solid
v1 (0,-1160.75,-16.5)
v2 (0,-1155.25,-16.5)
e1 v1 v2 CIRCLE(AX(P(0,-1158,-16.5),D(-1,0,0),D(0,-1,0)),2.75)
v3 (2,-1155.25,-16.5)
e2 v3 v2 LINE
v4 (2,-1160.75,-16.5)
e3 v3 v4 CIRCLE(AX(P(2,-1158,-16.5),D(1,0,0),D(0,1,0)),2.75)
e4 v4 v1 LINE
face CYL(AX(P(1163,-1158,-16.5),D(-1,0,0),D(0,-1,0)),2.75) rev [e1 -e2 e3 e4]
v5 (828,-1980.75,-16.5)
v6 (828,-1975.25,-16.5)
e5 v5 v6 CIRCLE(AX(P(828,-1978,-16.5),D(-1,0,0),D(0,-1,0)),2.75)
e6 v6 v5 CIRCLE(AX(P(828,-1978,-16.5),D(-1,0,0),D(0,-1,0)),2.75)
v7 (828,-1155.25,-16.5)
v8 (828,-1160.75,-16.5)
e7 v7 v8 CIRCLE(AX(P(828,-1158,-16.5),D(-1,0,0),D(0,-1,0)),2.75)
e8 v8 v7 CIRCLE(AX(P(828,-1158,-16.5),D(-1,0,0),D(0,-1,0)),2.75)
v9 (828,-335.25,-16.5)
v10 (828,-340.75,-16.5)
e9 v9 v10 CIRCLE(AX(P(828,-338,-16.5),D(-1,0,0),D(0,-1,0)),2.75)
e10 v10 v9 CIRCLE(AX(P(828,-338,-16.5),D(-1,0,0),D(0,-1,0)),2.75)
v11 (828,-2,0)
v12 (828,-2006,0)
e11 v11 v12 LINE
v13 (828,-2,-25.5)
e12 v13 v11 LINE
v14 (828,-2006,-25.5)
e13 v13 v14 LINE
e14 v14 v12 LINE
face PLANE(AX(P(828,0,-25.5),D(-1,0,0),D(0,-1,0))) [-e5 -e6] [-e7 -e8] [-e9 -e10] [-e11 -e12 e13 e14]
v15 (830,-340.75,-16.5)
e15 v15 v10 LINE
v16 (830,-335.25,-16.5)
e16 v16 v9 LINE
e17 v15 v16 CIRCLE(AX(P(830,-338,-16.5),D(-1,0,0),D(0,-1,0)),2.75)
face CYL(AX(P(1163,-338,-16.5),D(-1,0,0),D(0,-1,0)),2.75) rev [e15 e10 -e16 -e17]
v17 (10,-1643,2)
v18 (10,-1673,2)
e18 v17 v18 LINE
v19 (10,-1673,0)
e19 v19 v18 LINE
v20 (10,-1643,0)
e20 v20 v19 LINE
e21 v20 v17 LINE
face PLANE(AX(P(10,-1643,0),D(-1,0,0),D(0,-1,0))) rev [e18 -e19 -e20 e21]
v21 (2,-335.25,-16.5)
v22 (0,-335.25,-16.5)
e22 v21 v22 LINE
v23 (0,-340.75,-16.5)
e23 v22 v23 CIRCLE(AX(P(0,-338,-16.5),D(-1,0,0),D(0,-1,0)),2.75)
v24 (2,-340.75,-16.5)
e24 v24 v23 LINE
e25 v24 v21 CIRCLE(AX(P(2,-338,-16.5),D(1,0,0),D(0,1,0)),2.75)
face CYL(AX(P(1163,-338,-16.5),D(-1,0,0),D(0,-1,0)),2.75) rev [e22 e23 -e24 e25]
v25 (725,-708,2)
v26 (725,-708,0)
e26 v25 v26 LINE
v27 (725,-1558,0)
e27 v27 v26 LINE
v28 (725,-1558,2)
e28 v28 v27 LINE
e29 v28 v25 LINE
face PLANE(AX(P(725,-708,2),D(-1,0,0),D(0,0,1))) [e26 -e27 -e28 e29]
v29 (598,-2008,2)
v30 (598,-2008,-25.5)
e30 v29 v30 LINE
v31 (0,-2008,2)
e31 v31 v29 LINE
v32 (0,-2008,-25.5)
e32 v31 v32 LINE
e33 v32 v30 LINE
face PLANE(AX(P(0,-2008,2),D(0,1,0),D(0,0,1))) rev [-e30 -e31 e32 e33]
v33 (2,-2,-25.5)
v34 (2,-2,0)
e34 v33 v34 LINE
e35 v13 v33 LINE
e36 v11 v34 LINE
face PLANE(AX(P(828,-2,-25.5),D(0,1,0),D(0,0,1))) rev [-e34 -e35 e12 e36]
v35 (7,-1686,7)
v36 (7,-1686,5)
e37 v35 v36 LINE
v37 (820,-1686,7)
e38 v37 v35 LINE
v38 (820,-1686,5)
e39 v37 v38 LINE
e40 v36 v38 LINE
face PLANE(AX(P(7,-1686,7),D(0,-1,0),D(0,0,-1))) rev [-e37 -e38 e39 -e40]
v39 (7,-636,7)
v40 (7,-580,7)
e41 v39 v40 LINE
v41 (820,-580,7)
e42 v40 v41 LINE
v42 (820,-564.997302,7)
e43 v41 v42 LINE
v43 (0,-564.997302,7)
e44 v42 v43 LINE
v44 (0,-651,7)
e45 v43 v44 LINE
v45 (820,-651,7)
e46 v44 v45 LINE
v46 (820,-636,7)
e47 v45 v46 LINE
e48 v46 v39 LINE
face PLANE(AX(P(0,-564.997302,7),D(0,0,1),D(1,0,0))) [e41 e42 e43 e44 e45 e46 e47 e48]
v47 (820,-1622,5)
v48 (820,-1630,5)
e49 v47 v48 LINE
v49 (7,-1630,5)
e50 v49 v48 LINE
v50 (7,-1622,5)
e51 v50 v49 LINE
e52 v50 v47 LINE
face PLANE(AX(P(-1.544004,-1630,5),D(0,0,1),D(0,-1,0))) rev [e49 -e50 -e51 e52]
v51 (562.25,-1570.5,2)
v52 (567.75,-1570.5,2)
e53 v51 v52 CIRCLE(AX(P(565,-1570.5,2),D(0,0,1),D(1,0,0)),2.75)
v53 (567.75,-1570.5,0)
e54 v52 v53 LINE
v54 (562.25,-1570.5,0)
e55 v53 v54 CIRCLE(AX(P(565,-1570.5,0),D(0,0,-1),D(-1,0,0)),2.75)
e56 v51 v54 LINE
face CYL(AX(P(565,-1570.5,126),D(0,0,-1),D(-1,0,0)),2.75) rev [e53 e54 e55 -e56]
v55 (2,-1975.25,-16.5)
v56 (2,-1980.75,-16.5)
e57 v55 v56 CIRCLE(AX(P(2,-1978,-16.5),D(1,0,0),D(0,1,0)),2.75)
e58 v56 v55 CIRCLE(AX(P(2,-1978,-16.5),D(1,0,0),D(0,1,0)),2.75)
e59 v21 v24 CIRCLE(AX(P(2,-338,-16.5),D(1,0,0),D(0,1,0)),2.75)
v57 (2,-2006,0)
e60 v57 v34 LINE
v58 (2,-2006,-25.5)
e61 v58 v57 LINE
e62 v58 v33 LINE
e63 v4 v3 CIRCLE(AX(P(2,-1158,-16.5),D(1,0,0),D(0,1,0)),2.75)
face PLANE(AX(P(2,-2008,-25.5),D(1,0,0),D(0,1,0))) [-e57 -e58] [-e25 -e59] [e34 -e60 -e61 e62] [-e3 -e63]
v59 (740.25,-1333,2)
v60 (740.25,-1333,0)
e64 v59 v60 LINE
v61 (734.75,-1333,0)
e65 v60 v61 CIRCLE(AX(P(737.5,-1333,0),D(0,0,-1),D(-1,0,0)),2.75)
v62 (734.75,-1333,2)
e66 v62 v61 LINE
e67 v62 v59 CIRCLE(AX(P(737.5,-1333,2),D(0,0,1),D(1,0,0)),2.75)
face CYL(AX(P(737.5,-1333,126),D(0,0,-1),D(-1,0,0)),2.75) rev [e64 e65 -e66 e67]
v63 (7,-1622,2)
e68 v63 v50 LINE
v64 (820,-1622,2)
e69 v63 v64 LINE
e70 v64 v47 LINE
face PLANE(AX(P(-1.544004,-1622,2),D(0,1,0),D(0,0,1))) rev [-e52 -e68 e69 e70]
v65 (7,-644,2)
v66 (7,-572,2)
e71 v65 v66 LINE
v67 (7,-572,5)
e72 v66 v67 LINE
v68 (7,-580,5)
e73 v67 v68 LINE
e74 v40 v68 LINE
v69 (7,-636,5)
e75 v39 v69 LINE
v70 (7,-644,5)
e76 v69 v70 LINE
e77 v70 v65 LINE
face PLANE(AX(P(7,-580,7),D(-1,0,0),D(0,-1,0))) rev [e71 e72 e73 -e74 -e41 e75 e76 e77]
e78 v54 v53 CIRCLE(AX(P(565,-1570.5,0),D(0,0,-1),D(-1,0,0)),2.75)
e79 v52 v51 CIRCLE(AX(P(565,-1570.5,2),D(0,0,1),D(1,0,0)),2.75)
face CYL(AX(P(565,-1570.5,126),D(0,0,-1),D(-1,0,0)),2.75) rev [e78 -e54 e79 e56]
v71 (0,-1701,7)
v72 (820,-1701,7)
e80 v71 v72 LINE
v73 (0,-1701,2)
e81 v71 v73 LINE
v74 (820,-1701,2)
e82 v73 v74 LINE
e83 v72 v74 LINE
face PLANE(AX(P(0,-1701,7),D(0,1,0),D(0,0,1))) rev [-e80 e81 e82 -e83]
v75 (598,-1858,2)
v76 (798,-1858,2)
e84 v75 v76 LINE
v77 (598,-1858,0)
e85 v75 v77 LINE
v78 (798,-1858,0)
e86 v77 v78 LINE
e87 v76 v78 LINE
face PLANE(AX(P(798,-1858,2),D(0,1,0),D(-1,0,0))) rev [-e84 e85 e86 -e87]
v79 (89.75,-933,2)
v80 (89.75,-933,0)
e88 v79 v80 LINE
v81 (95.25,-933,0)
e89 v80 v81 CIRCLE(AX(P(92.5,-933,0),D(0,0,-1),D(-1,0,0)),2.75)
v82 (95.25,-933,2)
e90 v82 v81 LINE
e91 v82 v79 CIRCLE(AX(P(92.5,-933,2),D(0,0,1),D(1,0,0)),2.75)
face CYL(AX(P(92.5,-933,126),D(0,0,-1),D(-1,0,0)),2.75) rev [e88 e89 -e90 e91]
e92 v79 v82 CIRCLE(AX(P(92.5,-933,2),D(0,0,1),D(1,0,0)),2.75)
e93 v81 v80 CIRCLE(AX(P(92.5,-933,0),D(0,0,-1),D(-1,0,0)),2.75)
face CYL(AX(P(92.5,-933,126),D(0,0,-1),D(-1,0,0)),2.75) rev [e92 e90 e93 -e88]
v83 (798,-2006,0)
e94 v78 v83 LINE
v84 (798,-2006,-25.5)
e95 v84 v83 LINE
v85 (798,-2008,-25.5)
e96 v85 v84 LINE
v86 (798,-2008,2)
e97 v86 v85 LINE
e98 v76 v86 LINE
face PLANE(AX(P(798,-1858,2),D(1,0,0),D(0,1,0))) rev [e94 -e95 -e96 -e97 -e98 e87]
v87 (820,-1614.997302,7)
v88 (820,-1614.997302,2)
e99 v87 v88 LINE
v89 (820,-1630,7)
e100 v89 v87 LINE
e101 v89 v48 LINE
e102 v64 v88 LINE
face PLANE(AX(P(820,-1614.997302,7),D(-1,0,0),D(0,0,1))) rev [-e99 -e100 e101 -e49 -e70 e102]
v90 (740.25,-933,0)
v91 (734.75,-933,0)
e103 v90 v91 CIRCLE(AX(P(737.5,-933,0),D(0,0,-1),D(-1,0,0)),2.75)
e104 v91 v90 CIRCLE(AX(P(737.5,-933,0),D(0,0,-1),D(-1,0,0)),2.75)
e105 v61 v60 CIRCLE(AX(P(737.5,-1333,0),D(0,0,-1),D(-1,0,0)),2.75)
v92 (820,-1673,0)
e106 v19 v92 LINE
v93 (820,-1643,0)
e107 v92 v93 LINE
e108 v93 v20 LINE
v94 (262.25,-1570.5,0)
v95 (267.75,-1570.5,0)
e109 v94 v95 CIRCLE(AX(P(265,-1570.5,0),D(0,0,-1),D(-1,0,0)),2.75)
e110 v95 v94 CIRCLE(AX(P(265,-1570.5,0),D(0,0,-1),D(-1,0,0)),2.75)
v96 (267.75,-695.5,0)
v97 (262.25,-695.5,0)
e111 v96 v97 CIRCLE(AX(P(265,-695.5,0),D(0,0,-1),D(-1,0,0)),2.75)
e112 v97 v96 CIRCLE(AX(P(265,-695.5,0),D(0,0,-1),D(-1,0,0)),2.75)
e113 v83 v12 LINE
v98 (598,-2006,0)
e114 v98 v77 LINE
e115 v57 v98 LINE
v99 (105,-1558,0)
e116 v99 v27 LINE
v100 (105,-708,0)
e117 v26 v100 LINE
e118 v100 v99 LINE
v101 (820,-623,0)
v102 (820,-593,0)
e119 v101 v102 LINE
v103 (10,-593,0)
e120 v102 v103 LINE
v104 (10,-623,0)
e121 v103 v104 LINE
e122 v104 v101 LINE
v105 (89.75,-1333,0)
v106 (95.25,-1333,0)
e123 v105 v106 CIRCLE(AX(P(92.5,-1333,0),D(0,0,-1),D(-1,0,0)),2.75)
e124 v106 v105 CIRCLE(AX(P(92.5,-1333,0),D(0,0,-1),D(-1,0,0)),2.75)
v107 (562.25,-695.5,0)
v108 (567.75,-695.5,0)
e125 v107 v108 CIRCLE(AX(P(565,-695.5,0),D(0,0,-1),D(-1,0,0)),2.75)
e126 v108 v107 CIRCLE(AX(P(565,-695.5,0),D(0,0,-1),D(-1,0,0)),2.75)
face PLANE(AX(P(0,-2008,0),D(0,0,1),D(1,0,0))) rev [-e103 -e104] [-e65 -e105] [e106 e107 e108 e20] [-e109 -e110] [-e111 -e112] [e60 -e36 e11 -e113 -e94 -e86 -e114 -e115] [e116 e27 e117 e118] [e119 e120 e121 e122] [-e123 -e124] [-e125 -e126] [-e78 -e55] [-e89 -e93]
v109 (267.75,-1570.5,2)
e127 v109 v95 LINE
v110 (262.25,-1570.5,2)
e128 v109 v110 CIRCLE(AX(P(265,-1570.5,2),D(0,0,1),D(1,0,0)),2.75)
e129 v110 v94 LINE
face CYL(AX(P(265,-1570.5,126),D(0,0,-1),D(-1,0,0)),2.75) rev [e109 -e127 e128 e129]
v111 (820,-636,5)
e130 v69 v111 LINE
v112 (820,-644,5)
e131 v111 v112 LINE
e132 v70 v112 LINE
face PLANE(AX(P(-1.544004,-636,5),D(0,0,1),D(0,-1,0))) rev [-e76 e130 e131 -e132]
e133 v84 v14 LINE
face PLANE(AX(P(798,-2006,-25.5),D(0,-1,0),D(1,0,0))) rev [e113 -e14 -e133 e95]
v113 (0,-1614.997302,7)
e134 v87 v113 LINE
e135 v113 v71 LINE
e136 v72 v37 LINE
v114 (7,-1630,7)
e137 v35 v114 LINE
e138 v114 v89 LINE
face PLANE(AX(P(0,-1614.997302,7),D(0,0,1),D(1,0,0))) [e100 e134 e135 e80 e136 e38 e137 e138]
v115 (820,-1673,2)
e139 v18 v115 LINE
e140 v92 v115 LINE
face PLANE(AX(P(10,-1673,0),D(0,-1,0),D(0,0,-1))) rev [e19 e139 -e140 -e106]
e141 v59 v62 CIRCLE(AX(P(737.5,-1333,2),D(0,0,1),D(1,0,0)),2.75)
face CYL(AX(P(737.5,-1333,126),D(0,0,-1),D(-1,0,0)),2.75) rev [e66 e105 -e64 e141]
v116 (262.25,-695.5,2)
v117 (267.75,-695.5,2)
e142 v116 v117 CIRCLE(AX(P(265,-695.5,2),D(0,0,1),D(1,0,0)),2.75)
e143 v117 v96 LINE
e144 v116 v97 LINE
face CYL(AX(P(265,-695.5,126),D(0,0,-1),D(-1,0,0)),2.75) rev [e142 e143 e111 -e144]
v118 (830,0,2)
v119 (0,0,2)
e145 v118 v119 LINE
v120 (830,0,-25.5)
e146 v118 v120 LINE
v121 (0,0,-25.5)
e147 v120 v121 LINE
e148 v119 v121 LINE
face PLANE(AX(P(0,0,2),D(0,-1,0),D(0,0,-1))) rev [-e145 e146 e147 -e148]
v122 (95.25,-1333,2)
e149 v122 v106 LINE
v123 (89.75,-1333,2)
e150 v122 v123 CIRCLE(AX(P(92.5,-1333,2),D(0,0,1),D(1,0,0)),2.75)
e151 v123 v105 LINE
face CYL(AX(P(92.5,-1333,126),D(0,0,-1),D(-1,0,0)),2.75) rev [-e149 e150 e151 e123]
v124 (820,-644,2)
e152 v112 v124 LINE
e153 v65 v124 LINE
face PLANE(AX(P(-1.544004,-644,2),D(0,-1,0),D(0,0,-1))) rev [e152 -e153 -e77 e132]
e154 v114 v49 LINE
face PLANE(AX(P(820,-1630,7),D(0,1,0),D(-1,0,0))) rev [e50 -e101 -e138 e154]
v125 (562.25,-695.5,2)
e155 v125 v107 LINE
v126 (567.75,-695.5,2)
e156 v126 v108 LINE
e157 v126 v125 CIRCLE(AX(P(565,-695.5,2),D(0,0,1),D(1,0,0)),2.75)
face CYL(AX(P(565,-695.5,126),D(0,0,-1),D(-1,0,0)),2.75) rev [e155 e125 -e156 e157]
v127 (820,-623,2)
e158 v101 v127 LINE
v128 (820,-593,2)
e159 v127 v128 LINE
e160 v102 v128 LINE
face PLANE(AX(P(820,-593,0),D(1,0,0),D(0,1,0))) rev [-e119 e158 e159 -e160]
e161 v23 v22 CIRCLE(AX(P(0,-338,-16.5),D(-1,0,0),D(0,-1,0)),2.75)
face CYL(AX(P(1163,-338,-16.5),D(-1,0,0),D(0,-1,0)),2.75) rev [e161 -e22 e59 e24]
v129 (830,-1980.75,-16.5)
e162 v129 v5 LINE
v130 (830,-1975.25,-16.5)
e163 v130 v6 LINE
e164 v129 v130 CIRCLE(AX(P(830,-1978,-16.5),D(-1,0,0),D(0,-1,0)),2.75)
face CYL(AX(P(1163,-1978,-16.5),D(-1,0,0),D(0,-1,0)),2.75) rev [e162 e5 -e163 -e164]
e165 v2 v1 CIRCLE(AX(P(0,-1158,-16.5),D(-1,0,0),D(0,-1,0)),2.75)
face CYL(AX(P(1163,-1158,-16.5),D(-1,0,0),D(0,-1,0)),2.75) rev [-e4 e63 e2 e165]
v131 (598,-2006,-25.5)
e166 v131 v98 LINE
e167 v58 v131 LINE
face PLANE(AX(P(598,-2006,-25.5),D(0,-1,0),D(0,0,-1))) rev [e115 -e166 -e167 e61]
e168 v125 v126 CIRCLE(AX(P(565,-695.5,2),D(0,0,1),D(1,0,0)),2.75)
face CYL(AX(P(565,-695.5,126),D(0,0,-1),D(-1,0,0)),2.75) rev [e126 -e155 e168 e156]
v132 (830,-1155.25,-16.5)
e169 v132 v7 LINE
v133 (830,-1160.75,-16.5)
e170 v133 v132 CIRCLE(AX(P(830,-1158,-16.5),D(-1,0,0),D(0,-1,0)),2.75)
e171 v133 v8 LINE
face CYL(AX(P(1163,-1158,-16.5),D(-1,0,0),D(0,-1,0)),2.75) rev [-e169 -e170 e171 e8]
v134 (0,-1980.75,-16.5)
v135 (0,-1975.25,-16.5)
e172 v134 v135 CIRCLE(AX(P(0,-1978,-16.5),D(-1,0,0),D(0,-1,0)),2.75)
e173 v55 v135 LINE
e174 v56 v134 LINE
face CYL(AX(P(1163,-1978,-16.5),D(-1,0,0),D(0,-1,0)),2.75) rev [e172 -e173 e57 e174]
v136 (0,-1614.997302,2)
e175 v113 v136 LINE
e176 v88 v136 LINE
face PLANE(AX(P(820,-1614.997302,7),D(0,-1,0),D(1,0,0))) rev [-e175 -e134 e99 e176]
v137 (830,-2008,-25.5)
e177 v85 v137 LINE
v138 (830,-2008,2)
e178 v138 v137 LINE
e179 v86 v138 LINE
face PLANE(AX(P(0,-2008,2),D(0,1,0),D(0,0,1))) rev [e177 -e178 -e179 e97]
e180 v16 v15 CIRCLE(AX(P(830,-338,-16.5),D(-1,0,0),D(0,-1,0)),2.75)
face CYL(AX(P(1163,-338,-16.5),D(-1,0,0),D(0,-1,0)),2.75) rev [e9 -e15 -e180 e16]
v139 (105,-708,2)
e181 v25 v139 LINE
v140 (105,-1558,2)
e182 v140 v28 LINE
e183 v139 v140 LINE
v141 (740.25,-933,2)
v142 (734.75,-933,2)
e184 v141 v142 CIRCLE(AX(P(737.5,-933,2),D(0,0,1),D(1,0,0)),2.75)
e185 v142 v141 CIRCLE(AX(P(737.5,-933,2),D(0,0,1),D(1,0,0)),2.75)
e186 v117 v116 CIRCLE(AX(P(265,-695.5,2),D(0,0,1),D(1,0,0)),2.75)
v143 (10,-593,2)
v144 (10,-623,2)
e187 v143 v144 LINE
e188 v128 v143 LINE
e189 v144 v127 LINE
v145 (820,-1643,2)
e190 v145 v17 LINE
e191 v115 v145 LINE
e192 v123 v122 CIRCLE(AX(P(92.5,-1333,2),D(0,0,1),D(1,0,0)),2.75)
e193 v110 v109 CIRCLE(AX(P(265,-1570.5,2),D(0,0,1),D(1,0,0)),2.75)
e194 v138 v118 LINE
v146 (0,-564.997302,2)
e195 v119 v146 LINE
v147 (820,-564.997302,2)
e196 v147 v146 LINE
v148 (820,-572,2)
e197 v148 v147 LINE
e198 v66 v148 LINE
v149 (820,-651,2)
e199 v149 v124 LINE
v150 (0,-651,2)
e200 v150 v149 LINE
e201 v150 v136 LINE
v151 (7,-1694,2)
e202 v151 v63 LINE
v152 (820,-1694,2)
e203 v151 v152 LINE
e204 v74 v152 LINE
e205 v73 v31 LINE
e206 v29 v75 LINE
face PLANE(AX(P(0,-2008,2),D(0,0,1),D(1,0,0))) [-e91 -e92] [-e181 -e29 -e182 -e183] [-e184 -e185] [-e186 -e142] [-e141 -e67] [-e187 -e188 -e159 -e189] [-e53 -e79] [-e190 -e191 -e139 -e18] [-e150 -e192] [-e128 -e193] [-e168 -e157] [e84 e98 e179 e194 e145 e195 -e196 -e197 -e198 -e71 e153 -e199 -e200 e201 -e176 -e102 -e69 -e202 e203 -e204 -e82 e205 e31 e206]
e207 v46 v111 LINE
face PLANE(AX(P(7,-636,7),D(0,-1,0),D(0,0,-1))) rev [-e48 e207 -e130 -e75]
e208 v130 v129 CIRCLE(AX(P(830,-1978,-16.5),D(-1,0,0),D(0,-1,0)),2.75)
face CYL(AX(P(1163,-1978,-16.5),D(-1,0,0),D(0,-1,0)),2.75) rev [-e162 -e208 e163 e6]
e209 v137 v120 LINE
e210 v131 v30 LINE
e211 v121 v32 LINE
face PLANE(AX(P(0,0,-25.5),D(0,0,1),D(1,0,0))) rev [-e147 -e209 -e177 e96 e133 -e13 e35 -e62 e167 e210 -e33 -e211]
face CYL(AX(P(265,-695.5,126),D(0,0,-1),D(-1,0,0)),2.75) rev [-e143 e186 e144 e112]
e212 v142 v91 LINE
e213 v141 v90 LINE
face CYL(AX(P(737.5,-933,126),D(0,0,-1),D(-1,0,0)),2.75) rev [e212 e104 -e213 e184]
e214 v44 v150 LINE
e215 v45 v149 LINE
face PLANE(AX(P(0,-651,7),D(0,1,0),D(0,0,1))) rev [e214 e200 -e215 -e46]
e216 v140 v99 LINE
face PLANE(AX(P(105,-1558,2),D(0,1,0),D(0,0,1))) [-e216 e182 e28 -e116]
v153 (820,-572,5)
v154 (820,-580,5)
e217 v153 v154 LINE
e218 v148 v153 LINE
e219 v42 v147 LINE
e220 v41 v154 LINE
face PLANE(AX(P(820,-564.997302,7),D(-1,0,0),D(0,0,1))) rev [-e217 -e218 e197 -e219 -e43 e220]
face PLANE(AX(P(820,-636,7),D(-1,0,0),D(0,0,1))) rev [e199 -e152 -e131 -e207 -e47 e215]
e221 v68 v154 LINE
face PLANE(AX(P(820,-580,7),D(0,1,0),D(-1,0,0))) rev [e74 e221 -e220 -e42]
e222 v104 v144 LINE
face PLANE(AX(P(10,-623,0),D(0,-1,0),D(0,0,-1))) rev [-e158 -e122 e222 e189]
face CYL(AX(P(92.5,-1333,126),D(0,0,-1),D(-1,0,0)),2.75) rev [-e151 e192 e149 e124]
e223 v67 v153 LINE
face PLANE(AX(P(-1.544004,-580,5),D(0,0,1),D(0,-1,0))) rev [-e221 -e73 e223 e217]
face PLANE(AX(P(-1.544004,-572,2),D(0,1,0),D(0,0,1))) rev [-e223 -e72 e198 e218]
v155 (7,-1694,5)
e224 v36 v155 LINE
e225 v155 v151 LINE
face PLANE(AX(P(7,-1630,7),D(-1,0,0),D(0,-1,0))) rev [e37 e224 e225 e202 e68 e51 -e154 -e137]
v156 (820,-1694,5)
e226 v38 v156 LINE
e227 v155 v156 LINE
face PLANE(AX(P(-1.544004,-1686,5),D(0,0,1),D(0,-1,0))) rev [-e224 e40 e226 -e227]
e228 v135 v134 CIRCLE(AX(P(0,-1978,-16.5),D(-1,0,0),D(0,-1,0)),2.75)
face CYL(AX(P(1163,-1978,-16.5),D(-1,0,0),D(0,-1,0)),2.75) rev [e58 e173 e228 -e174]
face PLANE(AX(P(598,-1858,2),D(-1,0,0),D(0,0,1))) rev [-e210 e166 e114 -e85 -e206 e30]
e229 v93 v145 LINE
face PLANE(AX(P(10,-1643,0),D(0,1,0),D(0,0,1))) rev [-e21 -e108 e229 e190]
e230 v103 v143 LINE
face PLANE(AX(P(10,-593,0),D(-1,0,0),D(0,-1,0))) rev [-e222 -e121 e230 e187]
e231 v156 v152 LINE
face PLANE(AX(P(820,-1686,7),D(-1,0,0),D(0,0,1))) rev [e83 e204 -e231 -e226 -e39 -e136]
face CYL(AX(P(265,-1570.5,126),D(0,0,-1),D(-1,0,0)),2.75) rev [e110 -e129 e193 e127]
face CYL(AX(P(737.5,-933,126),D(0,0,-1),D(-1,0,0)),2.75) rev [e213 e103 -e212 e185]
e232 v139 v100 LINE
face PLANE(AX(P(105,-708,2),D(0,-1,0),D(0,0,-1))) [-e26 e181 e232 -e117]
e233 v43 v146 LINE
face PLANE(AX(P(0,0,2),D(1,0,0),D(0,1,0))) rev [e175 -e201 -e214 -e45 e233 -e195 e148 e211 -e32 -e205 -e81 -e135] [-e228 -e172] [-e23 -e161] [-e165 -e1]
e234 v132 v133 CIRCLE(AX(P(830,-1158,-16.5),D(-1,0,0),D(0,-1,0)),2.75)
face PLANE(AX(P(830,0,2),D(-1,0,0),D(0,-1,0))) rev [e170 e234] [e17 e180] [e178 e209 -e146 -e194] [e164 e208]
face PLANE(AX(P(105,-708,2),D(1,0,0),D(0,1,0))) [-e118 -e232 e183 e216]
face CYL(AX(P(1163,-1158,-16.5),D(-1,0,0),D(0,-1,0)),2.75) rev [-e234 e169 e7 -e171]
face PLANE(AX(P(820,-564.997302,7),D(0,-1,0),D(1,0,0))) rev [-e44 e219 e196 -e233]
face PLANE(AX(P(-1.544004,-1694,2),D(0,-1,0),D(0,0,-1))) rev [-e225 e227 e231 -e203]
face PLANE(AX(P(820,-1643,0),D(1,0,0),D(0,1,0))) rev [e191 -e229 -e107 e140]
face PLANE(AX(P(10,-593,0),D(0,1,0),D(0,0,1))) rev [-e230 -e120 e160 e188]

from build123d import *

# Parameters (mm, degrees)
SKETCH_1_W             = 830
SKETCH_1_H             = 2008
SKETCH_1_W_2           = 620
SKETCH_1_H_2           = 850
EXTRUDE_1_DEPTH        = 2
SKETCH_2_W             = 810
SKETCH_2_H             = 30
CUT_EXTRUDE_1_DEPTH    = 2
SKETCH_3_W             = 2
SKETCH_3_H             = 2008
EXTRUDE_2_DEPTH        = 25.5
SKETCH_4_W             = 200
SKETCH_4_H             = 150
CUT_EXTRUDE_2_DEPTH    = 2173.927575875
SKETCH_5_W             = 30
SKETCH_5_H             = 2
SKETCH_5_W_2           = 596
SKETCH_5_W_3           = 826
EXTRUDE_3_DEPTH        = 25.5
EXTRUDE_4_DEPTH        = 5
SKETCH_8_W             = 3
SKETCH_8_H             = 8
CUT_EXTRUDE_3_DEPTH    = 813
PATTERN_LINEAR_1_COUNT = 2
PATTERN_LINEAR_1_PITCH = 1050
SKETCH_9_R             = 2.75
CUT_EXTRUDE_4_DEPTH    = 126
SKETCH_10_R            = 2.75
CUT_EXTRUDE_5_DEPTH    = 1163


with BuildPart() as part:
    # 草图1 → 凸台-拉伸1 (new body)
    with BuildSketch(Plane.XY):
        with Locations((415, -1004)):
            Rectangle(SKETCH_1_W, SKETCH_1_H)
        with Locations((415, -1133)):
            Rectangle(SKETCH_1_W_2, SKETCH_1_H_2, mode=Mode.SUBTRACT)
    extrude(amount=EXTRUDE_1_DEPTH)

    # 草图2 → 切除-拉伸1 (cut)
    with BuildSketch(Plane.XY.offset(2)):
        with Locations((415, -1658)):
            Rectangle(SKETCH_2_W, SKETCH_2_H)
        with Locations((415, -608)):
            Rectangle(SKETCH_2_W, SKETCH_2_H)
    extrude(amount=-CUT_EXTRUDE_1_DEPTH, mode=Mode.SUBTRACT)

    # 草图3 → 凸台-拉伸2 (add)
    with BuildSketch(Plane.XY):
        with Locations((1, -1004)):
            Rectangle(SKETCH_3_W, SKETCH_3_H)
        with Locations((829, -1004)):
            Rectangle(SKETCH_3_W, SKETCH_3_H)
    extrude(amount=-EXTRUDE_2_DEPTH)

    # 草图4 → 切除-拉伸2 (cut, through all)
    with BuildSketch(Plane(origin=(0, 0, 0), x_dir=(-1, 0, 0), z_dir=(0, 0, -1))):
        with Locations((-698, -1933)):
            Rectangle(SKETCH_4_W, SKETCH_4_H)
    extrude(amount=-CUT_EXTRUDE_2_DEPTH, mode=Mode.SUBTRACT)

    # 草图5 → 凸台-拉伸3 (add)
    with BuildSketch(Plane(origin=(0, 0, 0), x_dir=(-1, 0, 0), z_dir=(0, 0, -1))):
        with Locations((-813, -2007)):
            Rectangle(SKETCH_5_W, SKETCH_5_H)
        with Locations((-300, -2007)):
            Rectangle(SKETCH_5_W_2, SKETCH_5_H)
        with Locations((-415, -1)):
            Rectangle(SKETCH_5_W_3, SKETCH_5_H)
    extrude(amount=EXTRUDE_3_DEPTH)

    # 草图7 → 凸台-拉伸4 (add)
    with BuildSketch(Plane.XY.offset(2)):
        Polygon((820, -564.997302091), (820, -580), (7, -580), (7, -636), (820, -636), (820, -651), (0, -651), (0, -564.997302091), align=None)
    extrude_4 = extrude(amount=EXTRUDE_4_DEPTH)

    # 草图8 → 切除-拉伸3 (cut)
    with BuildSketch(Plane(origin=(820, 0, 0), x_dir=(0, 0, -1), z_dir=(1, 0, 0))):
        with Locations((-3.5, -576)):
            Rectangle(SKETCH_8_W, SKETCH_8_H)
        with Locations((-3.5, -640)):
            Rectangle(SKETCH_8_W, SKETCH_8_H)
    cut_extrude_3 = extrude(amount=-CUT_EXTRUDE_3_DEPTH, mode=Mode.SUBTRACT)

    # 阵列(线性)1: 凸台-拉伸4, 切除-拉伸3 ×2
    with Locations(*[(0, -i * PATTERN_LINEAR_1_PITCH, 0) for i in range(1, PATTERN_LINEAR_1_COUNT)]):
        add(extrude_4)
        add(cut_extrude_3, mode=Mode.SUBTRACT)

    # 草图9 → 切除-拉伸4 (cut)
    with BuildSketch(Plane(origin=(0, 0, 0), x_dir=(-1, 0, 0), z_dir=(0, 0, -1))):
        with Locations((-565, -695.5)):
            Circle(SKETCH_9_R)
        with Locations((-265, -695.5)):
            Circle(SKETCH_9_R)
        with Locations((-737.5, -933)):
            Circle(SKETCH_9_R)
        with Locations((-737.5, -1333)):
            Circle(SKETCH_9_R)
        with Locations((-565, -1570.5)):
            Circle(SKETCH_9_R)
        with Locations((-265, -1570.5)):
            Circle(SKETCH_9_R)
        with Locations((-92.5, -1333)):
            Circle(SKETCH_9_R)
        with Locations((-92.5, -933)):
            Circle(SKETCH_9_R)
    extrude(amount=-CUT_EXTRUDE_4_DEPTH, mode=Mode.SUBTRACT)

    # 草图10 → 切除-拉伸5 (cut)
    with BuildSketch(Plane.ZY):
        with Locations(Location((-16.5, -1978, 0), (0, 0, 270))):
            Circle(SKETCH_10_R)
        with Locations(Location((-16.5, -1158, 0), (0, 0, 270))):
            Circle(SKETCH_10_R)
        with Locations(Location((-16.5, -338, 0), (0, 0, 270))):
            Circle(SKETCH_10_R)
    extrude(amount=-CUT_EXTRUDE_5_DEPTH, mode=Mode.SUBTRACT)


solid = part.part
